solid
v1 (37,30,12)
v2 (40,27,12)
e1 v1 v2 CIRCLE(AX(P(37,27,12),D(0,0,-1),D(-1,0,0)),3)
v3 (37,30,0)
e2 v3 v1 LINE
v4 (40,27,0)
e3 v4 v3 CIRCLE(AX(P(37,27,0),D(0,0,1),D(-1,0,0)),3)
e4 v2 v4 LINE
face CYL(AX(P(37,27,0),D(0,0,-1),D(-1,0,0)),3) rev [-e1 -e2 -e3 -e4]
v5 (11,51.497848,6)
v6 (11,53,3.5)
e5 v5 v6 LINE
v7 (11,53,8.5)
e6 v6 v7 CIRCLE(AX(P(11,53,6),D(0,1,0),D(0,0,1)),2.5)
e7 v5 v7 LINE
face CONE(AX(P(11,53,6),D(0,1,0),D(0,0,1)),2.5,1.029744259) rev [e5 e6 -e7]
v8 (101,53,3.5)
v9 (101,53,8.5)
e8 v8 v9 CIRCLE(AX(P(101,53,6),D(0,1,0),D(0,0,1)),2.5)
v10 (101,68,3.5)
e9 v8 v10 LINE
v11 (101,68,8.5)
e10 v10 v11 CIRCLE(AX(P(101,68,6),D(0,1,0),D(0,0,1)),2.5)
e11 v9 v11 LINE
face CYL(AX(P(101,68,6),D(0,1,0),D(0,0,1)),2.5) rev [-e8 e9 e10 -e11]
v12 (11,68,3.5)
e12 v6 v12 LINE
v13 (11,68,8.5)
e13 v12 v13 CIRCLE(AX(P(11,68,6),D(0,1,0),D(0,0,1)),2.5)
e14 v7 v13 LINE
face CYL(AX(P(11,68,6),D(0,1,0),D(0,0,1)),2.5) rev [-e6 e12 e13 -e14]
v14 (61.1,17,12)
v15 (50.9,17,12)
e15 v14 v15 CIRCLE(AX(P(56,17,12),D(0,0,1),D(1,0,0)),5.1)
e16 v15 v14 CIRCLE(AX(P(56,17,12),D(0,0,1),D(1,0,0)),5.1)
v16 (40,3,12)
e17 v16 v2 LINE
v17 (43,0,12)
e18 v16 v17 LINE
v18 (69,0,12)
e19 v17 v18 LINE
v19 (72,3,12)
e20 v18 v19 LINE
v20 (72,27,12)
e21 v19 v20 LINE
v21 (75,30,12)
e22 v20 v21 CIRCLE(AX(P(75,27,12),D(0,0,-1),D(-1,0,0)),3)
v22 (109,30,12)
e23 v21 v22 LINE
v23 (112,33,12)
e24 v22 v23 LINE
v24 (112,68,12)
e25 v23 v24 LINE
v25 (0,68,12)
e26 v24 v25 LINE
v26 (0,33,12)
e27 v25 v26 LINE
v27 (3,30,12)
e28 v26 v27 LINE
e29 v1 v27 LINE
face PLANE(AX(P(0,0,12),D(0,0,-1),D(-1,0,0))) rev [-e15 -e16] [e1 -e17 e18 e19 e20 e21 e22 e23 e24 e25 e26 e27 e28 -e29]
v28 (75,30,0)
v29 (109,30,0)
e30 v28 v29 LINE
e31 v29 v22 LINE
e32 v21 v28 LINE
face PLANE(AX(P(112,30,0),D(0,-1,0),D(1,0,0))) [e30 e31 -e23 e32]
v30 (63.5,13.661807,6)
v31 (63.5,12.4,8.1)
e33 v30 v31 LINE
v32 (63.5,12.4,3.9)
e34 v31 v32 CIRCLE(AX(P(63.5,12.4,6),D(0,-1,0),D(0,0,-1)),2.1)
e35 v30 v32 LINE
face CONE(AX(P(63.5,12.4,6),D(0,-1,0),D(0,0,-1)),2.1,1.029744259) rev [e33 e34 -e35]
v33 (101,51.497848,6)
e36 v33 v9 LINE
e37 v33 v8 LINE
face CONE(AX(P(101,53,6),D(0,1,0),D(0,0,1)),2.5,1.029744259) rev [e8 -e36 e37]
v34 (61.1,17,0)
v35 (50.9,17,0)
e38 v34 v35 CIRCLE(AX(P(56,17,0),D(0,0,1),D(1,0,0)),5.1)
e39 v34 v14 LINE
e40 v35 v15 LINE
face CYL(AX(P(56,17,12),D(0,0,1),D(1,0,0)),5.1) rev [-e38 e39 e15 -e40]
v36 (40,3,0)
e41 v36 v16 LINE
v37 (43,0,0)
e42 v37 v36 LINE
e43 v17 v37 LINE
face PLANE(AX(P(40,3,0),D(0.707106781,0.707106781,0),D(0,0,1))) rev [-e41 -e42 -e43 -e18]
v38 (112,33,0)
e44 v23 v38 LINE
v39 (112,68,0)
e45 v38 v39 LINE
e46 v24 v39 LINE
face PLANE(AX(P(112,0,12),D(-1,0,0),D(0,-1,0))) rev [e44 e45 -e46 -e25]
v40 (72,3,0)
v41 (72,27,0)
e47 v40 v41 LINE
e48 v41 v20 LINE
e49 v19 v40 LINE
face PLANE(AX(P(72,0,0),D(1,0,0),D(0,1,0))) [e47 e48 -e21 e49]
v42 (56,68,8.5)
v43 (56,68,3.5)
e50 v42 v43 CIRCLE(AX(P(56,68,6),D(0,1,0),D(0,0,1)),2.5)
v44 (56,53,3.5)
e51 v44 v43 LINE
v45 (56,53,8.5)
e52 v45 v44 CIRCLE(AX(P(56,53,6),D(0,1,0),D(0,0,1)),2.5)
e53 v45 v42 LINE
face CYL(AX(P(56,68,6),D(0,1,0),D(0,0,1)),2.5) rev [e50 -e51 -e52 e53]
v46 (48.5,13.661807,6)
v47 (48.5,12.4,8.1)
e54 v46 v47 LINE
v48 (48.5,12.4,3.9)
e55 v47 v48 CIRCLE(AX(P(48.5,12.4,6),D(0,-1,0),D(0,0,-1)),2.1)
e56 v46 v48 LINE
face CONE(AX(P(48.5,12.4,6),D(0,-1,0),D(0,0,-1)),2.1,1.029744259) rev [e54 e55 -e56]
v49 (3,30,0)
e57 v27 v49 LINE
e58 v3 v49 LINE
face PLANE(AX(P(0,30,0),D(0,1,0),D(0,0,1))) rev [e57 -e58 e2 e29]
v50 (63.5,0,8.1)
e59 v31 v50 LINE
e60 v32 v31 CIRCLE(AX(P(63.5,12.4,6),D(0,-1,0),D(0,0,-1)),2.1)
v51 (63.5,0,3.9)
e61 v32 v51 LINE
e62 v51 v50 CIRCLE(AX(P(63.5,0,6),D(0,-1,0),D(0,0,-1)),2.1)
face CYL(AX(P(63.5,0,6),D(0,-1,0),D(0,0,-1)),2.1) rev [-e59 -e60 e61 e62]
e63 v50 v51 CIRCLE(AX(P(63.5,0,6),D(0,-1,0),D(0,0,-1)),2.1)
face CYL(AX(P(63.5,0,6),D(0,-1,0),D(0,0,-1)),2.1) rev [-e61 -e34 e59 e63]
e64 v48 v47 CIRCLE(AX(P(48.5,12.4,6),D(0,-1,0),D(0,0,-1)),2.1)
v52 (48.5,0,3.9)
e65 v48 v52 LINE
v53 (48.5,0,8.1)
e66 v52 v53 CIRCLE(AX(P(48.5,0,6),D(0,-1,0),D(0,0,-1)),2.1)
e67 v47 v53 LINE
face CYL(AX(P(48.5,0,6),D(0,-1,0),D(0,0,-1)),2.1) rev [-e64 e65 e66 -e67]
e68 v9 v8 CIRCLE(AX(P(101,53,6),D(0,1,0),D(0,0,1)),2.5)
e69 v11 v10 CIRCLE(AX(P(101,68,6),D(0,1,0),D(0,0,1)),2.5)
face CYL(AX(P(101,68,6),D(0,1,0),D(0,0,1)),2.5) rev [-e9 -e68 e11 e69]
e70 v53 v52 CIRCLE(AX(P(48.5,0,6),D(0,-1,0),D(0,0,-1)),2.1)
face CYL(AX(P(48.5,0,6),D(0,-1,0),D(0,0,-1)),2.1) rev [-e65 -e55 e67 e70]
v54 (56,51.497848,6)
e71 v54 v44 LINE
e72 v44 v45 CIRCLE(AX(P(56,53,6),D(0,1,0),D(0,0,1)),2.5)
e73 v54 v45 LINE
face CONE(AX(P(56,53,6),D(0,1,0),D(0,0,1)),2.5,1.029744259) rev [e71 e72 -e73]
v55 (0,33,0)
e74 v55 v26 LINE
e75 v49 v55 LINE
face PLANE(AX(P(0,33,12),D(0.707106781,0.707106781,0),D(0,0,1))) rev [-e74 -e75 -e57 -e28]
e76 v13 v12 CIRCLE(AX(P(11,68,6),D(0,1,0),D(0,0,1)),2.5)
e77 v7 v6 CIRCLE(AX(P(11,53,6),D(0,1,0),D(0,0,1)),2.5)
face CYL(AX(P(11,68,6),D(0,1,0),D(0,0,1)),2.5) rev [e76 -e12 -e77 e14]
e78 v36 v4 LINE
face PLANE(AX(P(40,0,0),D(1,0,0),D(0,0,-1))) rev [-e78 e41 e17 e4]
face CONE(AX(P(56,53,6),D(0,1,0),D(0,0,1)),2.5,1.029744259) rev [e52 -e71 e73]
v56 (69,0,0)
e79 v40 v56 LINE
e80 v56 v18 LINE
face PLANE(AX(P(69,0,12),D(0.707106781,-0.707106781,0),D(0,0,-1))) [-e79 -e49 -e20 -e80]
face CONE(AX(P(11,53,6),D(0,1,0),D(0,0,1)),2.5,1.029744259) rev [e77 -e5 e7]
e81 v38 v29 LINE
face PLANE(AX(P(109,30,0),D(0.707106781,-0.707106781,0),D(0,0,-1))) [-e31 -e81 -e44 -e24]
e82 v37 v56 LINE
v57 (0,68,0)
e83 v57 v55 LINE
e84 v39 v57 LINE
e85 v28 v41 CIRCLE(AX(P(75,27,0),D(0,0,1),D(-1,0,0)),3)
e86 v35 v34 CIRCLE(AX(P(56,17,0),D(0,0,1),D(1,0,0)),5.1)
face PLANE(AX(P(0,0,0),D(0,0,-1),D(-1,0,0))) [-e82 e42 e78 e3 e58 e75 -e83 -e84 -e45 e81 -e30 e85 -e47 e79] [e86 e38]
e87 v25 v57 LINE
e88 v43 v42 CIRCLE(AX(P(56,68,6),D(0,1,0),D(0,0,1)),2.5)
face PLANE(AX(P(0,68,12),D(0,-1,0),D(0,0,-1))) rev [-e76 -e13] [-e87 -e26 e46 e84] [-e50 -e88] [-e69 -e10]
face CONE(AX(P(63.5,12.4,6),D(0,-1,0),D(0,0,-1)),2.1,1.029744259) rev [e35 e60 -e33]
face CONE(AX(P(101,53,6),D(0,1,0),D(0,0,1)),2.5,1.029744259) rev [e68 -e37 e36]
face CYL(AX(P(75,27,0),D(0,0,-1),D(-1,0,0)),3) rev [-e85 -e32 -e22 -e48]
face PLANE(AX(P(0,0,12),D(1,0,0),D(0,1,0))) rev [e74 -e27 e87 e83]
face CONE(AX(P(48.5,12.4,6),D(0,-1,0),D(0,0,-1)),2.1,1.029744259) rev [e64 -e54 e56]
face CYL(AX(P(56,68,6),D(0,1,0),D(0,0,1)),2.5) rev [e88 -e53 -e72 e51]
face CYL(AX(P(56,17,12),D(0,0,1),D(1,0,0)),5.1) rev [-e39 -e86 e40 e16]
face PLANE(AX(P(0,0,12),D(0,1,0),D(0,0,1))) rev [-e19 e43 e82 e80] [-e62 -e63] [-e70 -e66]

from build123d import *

# Parameters (mm, degrees)
SKETCH_1_W             = 112
SKETCH_1_H             = 68
EXTRUDE_1_DEPTH        = 12
SKETCH_2_W             = 40
SKETCH_2_H             = 30
CUT_EXTRUDE_1_DEPTH    = 12
HOLE_WIZARD_M12_1_D    = 10.2
CHAMFER_1_SIZE         = 3
FILLET_1_R             = 3
HOLE_WIZARD_M6_1_D     = 5
HOLE_WIZARD_M6_1_DEPTH = 15
HOLE_WIZARD_M6_1_TIP   = 1.502151548
HOLE_WIZARD_M5_1_D     = 4.2
HOLE_WIZARD_M5_1_DEPTH = 12.4
HOLE_WIZARD_M5_1_TIP   = 1.2618073


with BuildPart() as part:
    # 草图1 → 凸台-拉伸1 (new body)
    with BuildSketch(Plane.XY):
        with Locations((56, 34)):
            Rectangle(SKETCH_1_W, SKETCH_1_H)
    extrude(amount=EXTRUDE_1_DEPTH)

    # 草图2 → 切除-拉伸1 (cut)
    with BuildSketch(Plane.XY.offset(12)):
        with Locations((20, 15)):
            Rectangle(SKETCH_2_W, SKETCH_2_H)
    cut_extrude_1 = extrude(amount=-CUT_EXTRUDE_1_DEPTH, mode=Mode.SUBTRACT)

    # 镜向1: 切除-拉伸1 across plane
    add(cut_extrude_1.mirror(Plane.ZY.offset(-56)), mode=Mode.SUBTRACT)

    # M12 螺纹孔1 (through all)
    with Locations(Plane.XY.offset(12)):
        with Locations((56, 17)):
            Hole(HOLE_WIZARD_M12_1_D / 2)

    # 倒角1
    chamfer_1_edges = [part.edges().sort_by_distance(p)[0] for p in [
        (0, 30, 6),
        (40, 0, 6),
        (112, 30, 6),
        (72, 0, 6),
    ]]
    chamfer(chamfer_1_edges, length=CHAMFER_1_SIZE)

    # 圆角1
    fillet_1_edges = [part.edges().sort_by_distance(p)[0] for p in [
        (40, 30, 6),
        (72, 30, 6),
    ]]
    fillet(fillet_1_edges, radius=FILLET_1_R)

    # M6 螺纹孔1
    with Locations(Plane(origin=(0, 68, 0), x_dir=(1, 0, 0), z_dir=(0, 1, 0))):
        with Locations((101, -6), (56, -6), (11, -6)):
            Hole(HOLE_WIZARD_M6_1_D / 2, depth=HOLE_WIZARD_M6_1_DEPTH)
            with Locations((0, 0, -(HOLE_WIZARD_M6_1_DEPTH + HOLE_WIZARD_M6_1_TIP / 2))):  # 118° drill point
                Cone(0, HOLE_WIZARD_M6_1_D / 2, HOLE_WIZARD_M6_1_TIP, mode=Mode.SUBTRACT)

    # M5 螺纹孔1
    with Locations(Plane(origin=(0, 0, 0), x_dir=(-1, 0, 0), z_dir=(0, -1, 0))):
        with Locations((-63.5, -6), (-48.5, -6)):
            Hole(HOLE_WIZARD_M5_1_D / 2, depth=HOLE_WIZARD_M5_1_DEPTH)
            with Locations((0, 0, -(HOLE_WIZARD_M5_1_DEPTH + HOLE_WIZARD_M5_1_TIP / 2))):  # 118° drill point
                Cone(0, HOLE_WIZARD_M5_1_D / 2, HOLE_WIZARD_M5_1_TIP, mode=Mode.SUBTRACT)


solid = part.part
